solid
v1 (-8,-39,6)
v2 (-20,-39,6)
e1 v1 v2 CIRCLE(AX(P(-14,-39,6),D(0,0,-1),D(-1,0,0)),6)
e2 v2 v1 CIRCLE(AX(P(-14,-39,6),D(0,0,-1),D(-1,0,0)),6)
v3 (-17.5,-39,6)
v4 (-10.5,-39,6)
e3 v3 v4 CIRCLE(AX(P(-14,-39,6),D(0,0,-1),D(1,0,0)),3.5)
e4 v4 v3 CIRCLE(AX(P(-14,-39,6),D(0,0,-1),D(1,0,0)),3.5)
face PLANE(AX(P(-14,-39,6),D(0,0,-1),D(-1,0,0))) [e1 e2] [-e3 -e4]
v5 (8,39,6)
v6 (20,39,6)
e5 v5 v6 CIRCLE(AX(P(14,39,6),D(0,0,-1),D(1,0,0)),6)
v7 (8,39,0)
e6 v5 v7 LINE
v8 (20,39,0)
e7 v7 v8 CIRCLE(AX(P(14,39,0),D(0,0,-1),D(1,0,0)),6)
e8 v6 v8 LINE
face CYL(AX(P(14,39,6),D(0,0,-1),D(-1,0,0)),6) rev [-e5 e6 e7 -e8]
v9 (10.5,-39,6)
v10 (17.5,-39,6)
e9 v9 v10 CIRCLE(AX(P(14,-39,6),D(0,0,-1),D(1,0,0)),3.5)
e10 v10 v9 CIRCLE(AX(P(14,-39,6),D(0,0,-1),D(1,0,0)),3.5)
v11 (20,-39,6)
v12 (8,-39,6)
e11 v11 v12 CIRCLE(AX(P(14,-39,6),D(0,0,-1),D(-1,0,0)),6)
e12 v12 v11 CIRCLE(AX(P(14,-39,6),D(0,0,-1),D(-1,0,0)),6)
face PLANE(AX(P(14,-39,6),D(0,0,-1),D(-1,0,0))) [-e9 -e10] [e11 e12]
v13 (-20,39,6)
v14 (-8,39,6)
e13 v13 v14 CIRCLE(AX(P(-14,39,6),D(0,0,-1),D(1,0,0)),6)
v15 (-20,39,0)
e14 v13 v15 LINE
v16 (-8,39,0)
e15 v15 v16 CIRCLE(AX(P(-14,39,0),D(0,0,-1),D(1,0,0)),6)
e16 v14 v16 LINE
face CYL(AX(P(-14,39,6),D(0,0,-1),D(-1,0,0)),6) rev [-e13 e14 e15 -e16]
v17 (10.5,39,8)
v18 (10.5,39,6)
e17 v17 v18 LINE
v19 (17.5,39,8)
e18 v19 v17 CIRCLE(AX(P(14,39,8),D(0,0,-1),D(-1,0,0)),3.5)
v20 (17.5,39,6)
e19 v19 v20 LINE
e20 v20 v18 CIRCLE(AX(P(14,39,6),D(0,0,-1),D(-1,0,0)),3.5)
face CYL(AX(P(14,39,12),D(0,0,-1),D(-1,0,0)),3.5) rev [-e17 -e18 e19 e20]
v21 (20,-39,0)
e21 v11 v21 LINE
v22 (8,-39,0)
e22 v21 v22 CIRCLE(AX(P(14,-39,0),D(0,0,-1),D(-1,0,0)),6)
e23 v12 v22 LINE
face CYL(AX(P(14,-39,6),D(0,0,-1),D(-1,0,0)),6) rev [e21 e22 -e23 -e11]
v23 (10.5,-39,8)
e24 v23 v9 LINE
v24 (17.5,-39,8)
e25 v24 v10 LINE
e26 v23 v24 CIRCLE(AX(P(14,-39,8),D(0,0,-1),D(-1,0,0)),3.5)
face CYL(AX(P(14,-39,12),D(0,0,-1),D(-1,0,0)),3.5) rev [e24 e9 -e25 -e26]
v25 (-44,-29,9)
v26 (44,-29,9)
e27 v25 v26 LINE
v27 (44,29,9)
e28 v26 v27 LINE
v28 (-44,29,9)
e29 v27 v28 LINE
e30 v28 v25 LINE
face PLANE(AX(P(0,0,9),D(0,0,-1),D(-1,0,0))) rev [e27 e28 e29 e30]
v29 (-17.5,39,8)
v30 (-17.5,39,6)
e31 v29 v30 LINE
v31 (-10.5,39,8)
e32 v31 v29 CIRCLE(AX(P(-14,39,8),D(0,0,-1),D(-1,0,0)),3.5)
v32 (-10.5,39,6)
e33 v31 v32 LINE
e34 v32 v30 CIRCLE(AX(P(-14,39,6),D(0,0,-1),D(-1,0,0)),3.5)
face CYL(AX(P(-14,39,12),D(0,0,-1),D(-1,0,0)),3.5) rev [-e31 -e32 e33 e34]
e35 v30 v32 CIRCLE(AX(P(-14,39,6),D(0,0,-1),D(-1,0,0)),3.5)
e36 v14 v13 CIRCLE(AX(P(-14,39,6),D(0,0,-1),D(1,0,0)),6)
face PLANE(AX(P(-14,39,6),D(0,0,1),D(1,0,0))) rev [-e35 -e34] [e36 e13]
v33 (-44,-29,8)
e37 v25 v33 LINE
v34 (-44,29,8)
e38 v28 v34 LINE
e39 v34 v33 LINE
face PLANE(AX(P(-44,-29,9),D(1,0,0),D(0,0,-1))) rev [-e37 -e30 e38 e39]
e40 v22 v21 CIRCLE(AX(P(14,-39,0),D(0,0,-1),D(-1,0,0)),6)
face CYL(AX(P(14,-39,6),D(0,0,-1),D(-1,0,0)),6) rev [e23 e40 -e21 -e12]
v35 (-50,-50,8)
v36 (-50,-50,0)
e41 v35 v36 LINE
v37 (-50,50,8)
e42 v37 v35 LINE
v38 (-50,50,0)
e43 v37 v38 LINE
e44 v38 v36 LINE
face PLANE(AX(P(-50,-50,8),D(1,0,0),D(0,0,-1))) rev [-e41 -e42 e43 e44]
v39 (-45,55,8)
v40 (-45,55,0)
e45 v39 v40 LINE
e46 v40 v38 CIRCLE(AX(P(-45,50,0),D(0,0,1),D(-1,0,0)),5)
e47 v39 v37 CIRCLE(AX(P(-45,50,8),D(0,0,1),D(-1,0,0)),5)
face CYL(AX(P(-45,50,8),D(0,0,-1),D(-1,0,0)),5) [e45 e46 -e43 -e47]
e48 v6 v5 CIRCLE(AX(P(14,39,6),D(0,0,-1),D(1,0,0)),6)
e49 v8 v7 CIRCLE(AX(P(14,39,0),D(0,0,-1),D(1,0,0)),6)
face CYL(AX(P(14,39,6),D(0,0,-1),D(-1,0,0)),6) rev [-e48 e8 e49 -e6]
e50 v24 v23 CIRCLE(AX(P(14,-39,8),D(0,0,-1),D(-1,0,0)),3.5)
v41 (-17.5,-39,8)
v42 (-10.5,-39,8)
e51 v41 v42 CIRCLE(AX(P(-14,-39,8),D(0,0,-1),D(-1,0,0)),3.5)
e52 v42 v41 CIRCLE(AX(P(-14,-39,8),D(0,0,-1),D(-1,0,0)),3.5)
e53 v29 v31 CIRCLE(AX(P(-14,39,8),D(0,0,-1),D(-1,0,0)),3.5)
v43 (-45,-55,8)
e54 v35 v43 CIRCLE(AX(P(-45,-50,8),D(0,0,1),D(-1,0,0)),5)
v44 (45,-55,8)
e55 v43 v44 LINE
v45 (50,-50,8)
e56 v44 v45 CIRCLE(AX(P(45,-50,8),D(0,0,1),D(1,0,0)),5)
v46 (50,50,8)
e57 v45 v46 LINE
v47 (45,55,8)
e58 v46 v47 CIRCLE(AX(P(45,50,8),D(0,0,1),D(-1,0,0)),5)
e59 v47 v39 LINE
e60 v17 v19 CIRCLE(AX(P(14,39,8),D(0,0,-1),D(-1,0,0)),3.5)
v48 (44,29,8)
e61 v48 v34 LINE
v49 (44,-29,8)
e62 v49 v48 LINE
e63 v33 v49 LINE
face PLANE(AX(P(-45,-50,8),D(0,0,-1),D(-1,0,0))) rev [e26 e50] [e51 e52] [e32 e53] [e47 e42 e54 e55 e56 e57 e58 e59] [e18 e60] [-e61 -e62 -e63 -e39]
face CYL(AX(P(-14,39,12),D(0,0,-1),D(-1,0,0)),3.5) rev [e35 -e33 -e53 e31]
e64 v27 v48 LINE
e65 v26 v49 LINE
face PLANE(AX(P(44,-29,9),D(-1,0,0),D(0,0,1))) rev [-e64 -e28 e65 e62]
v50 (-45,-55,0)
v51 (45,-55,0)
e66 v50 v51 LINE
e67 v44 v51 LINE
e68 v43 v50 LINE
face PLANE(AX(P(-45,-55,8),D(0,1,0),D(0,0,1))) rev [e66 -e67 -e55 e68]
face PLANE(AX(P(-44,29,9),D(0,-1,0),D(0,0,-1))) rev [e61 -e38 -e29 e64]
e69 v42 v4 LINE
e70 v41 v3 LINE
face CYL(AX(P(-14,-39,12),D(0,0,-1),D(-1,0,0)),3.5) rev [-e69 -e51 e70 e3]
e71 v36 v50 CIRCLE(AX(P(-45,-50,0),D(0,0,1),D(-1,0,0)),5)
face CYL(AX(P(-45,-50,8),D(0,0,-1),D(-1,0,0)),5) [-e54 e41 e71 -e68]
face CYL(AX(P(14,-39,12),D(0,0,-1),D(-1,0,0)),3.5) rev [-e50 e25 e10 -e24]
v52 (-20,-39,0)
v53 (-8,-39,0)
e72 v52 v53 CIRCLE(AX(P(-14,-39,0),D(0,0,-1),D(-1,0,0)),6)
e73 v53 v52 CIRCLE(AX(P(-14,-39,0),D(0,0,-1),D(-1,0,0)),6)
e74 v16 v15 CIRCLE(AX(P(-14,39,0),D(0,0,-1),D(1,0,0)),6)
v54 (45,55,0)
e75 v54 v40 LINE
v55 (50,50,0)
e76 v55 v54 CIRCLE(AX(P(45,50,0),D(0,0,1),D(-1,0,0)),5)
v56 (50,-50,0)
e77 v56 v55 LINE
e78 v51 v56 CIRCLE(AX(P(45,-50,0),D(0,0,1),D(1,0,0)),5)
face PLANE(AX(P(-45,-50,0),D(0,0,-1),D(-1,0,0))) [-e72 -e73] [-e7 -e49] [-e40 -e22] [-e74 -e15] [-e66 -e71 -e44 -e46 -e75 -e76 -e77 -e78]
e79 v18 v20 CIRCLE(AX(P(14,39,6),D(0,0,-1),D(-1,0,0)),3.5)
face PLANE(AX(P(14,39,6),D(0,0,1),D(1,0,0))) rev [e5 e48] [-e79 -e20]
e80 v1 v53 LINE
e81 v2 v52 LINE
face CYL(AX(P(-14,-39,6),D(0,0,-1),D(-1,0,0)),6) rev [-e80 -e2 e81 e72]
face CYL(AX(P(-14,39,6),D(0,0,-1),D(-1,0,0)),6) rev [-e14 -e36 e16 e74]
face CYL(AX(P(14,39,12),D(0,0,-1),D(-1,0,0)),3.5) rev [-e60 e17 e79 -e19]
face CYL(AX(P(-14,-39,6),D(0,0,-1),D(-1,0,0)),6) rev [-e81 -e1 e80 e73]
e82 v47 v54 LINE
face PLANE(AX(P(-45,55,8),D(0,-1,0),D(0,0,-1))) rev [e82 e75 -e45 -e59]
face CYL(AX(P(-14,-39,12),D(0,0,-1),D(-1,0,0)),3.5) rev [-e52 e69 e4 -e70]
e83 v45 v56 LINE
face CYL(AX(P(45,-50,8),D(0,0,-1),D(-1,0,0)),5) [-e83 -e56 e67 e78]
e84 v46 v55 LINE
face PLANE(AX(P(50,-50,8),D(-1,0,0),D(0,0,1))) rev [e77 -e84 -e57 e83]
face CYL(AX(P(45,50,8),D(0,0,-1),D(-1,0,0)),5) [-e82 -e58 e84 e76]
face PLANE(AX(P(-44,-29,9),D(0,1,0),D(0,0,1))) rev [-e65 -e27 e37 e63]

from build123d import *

# Parameters (mm, degrees)
BOSS_EXTRUDE1_DEPTH = 8
SKETCH2_W           = 88
SKETCH2_H           = 58
BOSS_EXTRUDE2_DEPTH = 1
SKETCH4_R           = 6
CUT_EXTRUDE1_DEPTH  = 6
SKETCH5_R           = 3.5
CUT_EXTRUDE2_DEPTH  = 6


with BuildPart() as part:
    # Sketch1 → Boss-Extrude1 (new body)
    with BuildSketch(Plane.XY):
        with BuildLine():
            Line((-45, -55), (45, -55))
            ThreePointArc((45, -55), (48.535533906, -53.535533906), (50, -50))
            Line((50, -50), (50, 50))
            ThreePointArc((50, 50), (48.535533906, 53.535533906), (45, 55))
            Line((45, 55), (-45, 55))
            ThreePointArc((-45, 55), (-48.535533906, 53.535533906), (-50, 50))
            Line((-50, 50), (-50, -50))
            ThreePointArc((-50, -50), (-48.535533906, -53.535533906), (-45, -55))
        make_face()
    extrude(amount=BOSS_EXTRUDE1_DEPTH)

    # Sketch2 → Boss-Extrude2 (add)
    with BuildSketch(Plane.XY.offset(8)):
        Rectangle(SKETCH2_W, SKETCH2_H)
    extrude(amount=BOSS_EXTRUDE2_DEPTH)

    # Sketch4 → Cut-Extrude1 (cut)
    with BuildSketch(Plane(origin=(0, 0, 0), x_dir=(-1, 0, 0), z_dir=(0, 0, -1))):
        with Locations((-14, -39)):
            Circle(SKETCH4_R)
        with Locations((14, -39)):
            Circle(SKETCH4_R)
        with Locations(Location((14, 39, 0), (0, 0, 180))):
            Circle(SKETCH4_R)
        with Locations(Location((-14, 39, 0), (0, 0, 180))):
            Circle(SKETCH4_R)
    extrude(amount=-CUT_EXTRUDE1_DEPTH, mode=Mode.SUBTRACT)

    # Sketch5 → Cut-Extrude2 (cut)
    with BuildSketch(Plane(origin=(0, 0, 6), x_dir=(-1, 0, 0), z_dir=(0, 0, -1))):
        with Locations((-14, 39)):
            Circle(SKETCH5_R)
        with Locations((14, 39)):
            Circle(SKETCH5_R)
        with Locations((14, -39)):
            Circle(SKETCH5_R)
        with Locations((-14, -39)):
            Circle(SKETCH5_R)
    extrude(amount=-CUT_EXTRUDE2_DEPTH, mode=Mode.SUBTRACT)


solid = part.part
